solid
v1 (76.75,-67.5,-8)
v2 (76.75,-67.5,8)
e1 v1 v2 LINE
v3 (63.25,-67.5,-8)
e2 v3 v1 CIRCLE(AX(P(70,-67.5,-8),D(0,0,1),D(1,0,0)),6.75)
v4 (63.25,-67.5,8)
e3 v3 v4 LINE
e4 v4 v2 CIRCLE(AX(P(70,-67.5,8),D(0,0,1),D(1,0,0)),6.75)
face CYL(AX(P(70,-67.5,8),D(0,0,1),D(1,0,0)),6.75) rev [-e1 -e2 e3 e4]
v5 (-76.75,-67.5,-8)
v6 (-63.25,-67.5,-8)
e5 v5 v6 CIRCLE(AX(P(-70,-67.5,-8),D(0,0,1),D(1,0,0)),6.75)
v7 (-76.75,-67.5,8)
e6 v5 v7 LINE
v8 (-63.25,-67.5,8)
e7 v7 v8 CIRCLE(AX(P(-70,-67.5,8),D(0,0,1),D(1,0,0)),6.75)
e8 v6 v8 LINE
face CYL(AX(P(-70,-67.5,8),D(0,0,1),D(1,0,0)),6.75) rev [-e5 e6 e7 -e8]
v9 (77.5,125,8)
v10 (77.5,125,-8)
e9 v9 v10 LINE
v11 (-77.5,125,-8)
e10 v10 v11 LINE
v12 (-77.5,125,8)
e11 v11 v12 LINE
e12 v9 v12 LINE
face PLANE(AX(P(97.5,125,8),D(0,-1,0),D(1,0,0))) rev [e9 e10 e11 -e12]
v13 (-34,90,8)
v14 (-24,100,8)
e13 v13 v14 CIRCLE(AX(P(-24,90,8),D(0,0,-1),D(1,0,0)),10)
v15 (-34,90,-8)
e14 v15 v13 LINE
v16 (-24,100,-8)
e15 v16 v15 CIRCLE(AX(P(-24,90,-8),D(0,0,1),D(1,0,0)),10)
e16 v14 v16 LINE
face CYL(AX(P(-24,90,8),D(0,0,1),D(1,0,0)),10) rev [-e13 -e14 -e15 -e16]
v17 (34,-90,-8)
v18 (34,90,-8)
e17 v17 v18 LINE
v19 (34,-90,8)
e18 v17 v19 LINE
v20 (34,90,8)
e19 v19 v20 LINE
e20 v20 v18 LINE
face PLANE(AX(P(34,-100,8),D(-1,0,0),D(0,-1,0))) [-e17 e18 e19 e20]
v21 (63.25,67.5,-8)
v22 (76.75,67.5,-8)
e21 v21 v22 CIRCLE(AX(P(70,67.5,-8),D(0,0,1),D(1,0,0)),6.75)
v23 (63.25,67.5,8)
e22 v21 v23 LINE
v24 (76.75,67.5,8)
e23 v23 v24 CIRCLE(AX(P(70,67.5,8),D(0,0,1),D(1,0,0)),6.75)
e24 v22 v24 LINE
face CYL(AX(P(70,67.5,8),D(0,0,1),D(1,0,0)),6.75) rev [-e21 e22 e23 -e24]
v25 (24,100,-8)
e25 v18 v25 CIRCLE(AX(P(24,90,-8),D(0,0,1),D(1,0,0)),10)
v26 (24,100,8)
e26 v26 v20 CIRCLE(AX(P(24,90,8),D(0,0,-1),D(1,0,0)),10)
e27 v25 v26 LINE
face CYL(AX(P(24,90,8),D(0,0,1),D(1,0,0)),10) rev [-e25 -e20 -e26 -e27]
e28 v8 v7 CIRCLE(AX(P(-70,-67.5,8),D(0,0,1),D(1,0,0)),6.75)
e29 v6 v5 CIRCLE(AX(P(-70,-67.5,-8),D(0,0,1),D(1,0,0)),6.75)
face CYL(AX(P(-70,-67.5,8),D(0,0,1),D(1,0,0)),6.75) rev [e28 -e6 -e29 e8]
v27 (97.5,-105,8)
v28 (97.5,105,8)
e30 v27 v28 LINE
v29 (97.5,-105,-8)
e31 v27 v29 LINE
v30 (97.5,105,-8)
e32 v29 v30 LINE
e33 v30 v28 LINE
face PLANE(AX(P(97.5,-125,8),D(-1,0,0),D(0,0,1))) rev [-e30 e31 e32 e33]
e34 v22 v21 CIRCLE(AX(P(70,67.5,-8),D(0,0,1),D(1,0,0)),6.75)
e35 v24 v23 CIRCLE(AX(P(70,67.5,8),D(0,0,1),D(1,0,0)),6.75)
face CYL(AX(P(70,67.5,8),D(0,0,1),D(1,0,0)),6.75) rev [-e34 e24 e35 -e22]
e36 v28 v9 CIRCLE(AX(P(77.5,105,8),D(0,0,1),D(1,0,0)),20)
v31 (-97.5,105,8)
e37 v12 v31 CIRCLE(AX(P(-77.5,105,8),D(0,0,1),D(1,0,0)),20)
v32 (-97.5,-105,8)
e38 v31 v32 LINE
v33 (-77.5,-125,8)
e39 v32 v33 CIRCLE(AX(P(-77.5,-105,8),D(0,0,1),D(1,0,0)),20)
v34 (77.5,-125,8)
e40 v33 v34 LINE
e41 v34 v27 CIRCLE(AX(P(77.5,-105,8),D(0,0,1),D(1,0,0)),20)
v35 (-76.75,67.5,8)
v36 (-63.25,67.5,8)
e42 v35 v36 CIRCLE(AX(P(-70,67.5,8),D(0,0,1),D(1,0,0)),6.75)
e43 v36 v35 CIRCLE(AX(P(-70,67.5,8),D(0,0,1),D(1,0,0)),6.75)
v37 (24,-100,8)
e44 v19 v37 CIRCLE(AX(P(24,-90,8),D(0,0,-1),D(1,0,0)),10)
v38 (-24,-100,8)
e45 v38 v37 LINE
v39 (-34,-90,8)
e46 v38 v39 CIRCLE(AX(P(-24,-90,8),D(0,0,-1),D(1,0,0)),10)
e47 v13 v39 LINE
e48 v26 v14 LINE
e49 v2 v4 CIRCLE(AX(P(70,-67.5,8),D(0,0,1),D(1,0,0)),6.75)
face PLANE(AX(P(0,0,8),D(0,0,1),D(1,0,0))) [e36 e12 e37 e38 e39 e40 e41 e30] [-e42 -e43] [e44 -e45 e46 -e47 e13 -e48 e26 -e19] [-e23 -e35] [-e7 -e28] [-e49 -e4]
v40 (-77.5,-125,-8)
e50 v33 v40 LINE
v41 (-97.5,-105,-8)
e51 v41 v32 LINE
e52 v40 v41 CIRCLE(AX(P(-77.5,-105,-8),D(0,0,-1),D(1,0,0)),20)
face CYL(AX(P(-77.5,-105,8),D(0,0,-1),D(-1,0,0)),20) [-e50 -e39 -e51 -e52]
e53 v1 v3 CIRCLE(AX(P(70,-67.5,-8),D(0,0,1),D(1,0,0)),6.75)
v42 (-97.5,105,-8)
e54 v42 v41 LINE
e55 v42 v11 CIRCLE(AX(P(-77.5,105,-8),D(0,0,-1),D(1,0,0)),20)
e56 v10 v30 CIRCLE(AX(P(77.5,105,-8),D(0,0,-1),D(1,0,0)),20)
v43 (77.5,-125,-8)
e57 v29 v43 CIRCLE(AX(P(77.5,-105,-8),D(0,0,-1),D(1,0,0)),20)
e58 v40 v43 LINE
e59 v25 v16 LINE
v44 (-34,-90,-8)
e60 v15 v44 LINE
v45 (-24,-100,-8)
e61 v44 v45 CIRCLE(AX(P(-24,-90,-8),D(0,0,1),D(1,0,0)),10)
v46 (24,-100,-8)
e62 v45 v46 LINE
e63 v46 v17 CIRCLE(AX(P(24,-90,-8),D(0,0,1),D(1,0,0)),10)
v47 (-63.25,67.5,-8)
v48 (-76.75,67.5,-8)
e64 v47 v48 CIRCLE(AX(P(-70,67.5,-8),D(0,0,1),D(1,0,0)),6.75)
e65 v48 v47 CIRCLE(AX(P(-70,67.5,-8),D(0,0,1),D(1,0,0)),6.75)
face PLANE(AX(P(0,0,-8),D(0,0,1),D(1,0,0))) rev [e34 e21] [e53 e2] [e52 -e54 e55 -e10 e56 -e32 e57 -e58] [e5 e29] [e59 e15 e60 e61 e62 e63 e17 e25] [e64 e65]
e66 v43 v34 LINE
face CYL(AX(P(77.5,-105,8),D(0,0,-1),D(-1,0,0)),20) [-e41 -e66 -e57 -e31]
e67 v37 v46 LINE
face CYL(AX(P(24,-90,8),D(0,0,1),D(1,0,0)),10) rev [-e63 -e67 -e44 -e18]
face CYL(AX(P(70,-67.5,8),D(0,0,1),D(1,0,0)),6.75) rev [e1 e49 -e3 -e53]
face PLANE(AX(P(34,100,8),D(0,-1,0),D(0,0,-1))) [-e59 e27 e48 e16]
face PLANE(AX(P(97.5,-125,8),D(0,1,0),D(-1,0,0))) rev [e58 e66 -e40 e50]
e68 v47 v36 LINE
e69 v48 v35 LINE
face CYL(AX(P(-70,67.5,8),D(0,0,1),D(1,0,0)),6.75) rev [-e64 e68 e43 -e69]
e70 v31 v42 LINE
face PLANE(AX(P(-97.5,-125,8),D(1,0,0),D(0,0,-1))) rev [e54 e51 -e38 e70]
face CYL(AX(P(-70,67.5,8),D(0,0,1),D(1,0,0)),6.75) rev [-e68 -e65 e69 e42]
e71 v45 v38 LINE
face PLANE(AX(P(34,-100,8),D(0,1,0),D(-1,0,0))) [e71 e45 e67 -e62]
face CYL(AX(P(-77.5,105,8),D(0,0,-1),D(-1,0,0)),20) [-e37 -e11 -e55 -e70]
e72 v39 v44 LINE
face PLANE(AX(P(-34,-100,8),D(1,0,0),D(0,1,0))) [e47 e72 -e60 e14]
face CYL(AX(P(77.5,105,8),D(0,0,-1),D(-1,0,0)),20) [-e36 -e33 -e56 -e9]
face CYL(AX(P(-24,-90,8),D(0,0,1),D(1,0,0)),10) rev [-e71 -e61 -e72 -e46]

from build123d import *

# Parameters (mm, degrees)
SKETCH1_W           = 195
SKETCH1_H           = 250
SKETCH1_W_2         = 68
SKETCH1_H_2         = 200
BOSS_EXTRUDE1_DEPTH = 8
F_13_5_HOLE1_D      = 13.5
FILLET2_R           = 20
FILLET3_R           = 10


with BuildPart() as part:
    # Sketch1 → Boss-Extrude1 (new, symmetric)
    with BuildSketch(Plane.XY):
        Rectangle(SKETCH1_W, SKETCH1_H)
        Rectangle(SKETCH1_W_2, SKETCH1_H_2, mode=Mode.SUBTRACT)
    extrude(amount=BOSS_EXTRUDE1_DEPTH, both=True)

    # Ø13.5 Hole1 (through all)
    with Locations(Plane.XY.offset(8)):
        with Locations((-70, 67.5), (70, 67.5), (70, -67.5), (-70, -67.5)):
            Hole(F_13_5_HOLE1_D / 2)

    # Fillet2
    fillet2_edges = [part.edges().sort_by_distance(p)[0] for p in [
        (-97.5, 125, 0),
        (97.5, 125, 0),
        (97.5, -125, 0),
        (-97.5, -125, 0),
    ]]
    fillet(fillet2_edges, radius=FILLET2_R)

    # Fillet3
    fillet3_edges = [part.edges().sort_by_distance(p)[0] for p in [
        (-34, 100, 0),
        (-34, -100, 0),
        (34, -100, 0),
        (34, 100, 0),
    ]]
    fillet(fillet3_edges, radius=FILLET3_R)


solid = part.part
